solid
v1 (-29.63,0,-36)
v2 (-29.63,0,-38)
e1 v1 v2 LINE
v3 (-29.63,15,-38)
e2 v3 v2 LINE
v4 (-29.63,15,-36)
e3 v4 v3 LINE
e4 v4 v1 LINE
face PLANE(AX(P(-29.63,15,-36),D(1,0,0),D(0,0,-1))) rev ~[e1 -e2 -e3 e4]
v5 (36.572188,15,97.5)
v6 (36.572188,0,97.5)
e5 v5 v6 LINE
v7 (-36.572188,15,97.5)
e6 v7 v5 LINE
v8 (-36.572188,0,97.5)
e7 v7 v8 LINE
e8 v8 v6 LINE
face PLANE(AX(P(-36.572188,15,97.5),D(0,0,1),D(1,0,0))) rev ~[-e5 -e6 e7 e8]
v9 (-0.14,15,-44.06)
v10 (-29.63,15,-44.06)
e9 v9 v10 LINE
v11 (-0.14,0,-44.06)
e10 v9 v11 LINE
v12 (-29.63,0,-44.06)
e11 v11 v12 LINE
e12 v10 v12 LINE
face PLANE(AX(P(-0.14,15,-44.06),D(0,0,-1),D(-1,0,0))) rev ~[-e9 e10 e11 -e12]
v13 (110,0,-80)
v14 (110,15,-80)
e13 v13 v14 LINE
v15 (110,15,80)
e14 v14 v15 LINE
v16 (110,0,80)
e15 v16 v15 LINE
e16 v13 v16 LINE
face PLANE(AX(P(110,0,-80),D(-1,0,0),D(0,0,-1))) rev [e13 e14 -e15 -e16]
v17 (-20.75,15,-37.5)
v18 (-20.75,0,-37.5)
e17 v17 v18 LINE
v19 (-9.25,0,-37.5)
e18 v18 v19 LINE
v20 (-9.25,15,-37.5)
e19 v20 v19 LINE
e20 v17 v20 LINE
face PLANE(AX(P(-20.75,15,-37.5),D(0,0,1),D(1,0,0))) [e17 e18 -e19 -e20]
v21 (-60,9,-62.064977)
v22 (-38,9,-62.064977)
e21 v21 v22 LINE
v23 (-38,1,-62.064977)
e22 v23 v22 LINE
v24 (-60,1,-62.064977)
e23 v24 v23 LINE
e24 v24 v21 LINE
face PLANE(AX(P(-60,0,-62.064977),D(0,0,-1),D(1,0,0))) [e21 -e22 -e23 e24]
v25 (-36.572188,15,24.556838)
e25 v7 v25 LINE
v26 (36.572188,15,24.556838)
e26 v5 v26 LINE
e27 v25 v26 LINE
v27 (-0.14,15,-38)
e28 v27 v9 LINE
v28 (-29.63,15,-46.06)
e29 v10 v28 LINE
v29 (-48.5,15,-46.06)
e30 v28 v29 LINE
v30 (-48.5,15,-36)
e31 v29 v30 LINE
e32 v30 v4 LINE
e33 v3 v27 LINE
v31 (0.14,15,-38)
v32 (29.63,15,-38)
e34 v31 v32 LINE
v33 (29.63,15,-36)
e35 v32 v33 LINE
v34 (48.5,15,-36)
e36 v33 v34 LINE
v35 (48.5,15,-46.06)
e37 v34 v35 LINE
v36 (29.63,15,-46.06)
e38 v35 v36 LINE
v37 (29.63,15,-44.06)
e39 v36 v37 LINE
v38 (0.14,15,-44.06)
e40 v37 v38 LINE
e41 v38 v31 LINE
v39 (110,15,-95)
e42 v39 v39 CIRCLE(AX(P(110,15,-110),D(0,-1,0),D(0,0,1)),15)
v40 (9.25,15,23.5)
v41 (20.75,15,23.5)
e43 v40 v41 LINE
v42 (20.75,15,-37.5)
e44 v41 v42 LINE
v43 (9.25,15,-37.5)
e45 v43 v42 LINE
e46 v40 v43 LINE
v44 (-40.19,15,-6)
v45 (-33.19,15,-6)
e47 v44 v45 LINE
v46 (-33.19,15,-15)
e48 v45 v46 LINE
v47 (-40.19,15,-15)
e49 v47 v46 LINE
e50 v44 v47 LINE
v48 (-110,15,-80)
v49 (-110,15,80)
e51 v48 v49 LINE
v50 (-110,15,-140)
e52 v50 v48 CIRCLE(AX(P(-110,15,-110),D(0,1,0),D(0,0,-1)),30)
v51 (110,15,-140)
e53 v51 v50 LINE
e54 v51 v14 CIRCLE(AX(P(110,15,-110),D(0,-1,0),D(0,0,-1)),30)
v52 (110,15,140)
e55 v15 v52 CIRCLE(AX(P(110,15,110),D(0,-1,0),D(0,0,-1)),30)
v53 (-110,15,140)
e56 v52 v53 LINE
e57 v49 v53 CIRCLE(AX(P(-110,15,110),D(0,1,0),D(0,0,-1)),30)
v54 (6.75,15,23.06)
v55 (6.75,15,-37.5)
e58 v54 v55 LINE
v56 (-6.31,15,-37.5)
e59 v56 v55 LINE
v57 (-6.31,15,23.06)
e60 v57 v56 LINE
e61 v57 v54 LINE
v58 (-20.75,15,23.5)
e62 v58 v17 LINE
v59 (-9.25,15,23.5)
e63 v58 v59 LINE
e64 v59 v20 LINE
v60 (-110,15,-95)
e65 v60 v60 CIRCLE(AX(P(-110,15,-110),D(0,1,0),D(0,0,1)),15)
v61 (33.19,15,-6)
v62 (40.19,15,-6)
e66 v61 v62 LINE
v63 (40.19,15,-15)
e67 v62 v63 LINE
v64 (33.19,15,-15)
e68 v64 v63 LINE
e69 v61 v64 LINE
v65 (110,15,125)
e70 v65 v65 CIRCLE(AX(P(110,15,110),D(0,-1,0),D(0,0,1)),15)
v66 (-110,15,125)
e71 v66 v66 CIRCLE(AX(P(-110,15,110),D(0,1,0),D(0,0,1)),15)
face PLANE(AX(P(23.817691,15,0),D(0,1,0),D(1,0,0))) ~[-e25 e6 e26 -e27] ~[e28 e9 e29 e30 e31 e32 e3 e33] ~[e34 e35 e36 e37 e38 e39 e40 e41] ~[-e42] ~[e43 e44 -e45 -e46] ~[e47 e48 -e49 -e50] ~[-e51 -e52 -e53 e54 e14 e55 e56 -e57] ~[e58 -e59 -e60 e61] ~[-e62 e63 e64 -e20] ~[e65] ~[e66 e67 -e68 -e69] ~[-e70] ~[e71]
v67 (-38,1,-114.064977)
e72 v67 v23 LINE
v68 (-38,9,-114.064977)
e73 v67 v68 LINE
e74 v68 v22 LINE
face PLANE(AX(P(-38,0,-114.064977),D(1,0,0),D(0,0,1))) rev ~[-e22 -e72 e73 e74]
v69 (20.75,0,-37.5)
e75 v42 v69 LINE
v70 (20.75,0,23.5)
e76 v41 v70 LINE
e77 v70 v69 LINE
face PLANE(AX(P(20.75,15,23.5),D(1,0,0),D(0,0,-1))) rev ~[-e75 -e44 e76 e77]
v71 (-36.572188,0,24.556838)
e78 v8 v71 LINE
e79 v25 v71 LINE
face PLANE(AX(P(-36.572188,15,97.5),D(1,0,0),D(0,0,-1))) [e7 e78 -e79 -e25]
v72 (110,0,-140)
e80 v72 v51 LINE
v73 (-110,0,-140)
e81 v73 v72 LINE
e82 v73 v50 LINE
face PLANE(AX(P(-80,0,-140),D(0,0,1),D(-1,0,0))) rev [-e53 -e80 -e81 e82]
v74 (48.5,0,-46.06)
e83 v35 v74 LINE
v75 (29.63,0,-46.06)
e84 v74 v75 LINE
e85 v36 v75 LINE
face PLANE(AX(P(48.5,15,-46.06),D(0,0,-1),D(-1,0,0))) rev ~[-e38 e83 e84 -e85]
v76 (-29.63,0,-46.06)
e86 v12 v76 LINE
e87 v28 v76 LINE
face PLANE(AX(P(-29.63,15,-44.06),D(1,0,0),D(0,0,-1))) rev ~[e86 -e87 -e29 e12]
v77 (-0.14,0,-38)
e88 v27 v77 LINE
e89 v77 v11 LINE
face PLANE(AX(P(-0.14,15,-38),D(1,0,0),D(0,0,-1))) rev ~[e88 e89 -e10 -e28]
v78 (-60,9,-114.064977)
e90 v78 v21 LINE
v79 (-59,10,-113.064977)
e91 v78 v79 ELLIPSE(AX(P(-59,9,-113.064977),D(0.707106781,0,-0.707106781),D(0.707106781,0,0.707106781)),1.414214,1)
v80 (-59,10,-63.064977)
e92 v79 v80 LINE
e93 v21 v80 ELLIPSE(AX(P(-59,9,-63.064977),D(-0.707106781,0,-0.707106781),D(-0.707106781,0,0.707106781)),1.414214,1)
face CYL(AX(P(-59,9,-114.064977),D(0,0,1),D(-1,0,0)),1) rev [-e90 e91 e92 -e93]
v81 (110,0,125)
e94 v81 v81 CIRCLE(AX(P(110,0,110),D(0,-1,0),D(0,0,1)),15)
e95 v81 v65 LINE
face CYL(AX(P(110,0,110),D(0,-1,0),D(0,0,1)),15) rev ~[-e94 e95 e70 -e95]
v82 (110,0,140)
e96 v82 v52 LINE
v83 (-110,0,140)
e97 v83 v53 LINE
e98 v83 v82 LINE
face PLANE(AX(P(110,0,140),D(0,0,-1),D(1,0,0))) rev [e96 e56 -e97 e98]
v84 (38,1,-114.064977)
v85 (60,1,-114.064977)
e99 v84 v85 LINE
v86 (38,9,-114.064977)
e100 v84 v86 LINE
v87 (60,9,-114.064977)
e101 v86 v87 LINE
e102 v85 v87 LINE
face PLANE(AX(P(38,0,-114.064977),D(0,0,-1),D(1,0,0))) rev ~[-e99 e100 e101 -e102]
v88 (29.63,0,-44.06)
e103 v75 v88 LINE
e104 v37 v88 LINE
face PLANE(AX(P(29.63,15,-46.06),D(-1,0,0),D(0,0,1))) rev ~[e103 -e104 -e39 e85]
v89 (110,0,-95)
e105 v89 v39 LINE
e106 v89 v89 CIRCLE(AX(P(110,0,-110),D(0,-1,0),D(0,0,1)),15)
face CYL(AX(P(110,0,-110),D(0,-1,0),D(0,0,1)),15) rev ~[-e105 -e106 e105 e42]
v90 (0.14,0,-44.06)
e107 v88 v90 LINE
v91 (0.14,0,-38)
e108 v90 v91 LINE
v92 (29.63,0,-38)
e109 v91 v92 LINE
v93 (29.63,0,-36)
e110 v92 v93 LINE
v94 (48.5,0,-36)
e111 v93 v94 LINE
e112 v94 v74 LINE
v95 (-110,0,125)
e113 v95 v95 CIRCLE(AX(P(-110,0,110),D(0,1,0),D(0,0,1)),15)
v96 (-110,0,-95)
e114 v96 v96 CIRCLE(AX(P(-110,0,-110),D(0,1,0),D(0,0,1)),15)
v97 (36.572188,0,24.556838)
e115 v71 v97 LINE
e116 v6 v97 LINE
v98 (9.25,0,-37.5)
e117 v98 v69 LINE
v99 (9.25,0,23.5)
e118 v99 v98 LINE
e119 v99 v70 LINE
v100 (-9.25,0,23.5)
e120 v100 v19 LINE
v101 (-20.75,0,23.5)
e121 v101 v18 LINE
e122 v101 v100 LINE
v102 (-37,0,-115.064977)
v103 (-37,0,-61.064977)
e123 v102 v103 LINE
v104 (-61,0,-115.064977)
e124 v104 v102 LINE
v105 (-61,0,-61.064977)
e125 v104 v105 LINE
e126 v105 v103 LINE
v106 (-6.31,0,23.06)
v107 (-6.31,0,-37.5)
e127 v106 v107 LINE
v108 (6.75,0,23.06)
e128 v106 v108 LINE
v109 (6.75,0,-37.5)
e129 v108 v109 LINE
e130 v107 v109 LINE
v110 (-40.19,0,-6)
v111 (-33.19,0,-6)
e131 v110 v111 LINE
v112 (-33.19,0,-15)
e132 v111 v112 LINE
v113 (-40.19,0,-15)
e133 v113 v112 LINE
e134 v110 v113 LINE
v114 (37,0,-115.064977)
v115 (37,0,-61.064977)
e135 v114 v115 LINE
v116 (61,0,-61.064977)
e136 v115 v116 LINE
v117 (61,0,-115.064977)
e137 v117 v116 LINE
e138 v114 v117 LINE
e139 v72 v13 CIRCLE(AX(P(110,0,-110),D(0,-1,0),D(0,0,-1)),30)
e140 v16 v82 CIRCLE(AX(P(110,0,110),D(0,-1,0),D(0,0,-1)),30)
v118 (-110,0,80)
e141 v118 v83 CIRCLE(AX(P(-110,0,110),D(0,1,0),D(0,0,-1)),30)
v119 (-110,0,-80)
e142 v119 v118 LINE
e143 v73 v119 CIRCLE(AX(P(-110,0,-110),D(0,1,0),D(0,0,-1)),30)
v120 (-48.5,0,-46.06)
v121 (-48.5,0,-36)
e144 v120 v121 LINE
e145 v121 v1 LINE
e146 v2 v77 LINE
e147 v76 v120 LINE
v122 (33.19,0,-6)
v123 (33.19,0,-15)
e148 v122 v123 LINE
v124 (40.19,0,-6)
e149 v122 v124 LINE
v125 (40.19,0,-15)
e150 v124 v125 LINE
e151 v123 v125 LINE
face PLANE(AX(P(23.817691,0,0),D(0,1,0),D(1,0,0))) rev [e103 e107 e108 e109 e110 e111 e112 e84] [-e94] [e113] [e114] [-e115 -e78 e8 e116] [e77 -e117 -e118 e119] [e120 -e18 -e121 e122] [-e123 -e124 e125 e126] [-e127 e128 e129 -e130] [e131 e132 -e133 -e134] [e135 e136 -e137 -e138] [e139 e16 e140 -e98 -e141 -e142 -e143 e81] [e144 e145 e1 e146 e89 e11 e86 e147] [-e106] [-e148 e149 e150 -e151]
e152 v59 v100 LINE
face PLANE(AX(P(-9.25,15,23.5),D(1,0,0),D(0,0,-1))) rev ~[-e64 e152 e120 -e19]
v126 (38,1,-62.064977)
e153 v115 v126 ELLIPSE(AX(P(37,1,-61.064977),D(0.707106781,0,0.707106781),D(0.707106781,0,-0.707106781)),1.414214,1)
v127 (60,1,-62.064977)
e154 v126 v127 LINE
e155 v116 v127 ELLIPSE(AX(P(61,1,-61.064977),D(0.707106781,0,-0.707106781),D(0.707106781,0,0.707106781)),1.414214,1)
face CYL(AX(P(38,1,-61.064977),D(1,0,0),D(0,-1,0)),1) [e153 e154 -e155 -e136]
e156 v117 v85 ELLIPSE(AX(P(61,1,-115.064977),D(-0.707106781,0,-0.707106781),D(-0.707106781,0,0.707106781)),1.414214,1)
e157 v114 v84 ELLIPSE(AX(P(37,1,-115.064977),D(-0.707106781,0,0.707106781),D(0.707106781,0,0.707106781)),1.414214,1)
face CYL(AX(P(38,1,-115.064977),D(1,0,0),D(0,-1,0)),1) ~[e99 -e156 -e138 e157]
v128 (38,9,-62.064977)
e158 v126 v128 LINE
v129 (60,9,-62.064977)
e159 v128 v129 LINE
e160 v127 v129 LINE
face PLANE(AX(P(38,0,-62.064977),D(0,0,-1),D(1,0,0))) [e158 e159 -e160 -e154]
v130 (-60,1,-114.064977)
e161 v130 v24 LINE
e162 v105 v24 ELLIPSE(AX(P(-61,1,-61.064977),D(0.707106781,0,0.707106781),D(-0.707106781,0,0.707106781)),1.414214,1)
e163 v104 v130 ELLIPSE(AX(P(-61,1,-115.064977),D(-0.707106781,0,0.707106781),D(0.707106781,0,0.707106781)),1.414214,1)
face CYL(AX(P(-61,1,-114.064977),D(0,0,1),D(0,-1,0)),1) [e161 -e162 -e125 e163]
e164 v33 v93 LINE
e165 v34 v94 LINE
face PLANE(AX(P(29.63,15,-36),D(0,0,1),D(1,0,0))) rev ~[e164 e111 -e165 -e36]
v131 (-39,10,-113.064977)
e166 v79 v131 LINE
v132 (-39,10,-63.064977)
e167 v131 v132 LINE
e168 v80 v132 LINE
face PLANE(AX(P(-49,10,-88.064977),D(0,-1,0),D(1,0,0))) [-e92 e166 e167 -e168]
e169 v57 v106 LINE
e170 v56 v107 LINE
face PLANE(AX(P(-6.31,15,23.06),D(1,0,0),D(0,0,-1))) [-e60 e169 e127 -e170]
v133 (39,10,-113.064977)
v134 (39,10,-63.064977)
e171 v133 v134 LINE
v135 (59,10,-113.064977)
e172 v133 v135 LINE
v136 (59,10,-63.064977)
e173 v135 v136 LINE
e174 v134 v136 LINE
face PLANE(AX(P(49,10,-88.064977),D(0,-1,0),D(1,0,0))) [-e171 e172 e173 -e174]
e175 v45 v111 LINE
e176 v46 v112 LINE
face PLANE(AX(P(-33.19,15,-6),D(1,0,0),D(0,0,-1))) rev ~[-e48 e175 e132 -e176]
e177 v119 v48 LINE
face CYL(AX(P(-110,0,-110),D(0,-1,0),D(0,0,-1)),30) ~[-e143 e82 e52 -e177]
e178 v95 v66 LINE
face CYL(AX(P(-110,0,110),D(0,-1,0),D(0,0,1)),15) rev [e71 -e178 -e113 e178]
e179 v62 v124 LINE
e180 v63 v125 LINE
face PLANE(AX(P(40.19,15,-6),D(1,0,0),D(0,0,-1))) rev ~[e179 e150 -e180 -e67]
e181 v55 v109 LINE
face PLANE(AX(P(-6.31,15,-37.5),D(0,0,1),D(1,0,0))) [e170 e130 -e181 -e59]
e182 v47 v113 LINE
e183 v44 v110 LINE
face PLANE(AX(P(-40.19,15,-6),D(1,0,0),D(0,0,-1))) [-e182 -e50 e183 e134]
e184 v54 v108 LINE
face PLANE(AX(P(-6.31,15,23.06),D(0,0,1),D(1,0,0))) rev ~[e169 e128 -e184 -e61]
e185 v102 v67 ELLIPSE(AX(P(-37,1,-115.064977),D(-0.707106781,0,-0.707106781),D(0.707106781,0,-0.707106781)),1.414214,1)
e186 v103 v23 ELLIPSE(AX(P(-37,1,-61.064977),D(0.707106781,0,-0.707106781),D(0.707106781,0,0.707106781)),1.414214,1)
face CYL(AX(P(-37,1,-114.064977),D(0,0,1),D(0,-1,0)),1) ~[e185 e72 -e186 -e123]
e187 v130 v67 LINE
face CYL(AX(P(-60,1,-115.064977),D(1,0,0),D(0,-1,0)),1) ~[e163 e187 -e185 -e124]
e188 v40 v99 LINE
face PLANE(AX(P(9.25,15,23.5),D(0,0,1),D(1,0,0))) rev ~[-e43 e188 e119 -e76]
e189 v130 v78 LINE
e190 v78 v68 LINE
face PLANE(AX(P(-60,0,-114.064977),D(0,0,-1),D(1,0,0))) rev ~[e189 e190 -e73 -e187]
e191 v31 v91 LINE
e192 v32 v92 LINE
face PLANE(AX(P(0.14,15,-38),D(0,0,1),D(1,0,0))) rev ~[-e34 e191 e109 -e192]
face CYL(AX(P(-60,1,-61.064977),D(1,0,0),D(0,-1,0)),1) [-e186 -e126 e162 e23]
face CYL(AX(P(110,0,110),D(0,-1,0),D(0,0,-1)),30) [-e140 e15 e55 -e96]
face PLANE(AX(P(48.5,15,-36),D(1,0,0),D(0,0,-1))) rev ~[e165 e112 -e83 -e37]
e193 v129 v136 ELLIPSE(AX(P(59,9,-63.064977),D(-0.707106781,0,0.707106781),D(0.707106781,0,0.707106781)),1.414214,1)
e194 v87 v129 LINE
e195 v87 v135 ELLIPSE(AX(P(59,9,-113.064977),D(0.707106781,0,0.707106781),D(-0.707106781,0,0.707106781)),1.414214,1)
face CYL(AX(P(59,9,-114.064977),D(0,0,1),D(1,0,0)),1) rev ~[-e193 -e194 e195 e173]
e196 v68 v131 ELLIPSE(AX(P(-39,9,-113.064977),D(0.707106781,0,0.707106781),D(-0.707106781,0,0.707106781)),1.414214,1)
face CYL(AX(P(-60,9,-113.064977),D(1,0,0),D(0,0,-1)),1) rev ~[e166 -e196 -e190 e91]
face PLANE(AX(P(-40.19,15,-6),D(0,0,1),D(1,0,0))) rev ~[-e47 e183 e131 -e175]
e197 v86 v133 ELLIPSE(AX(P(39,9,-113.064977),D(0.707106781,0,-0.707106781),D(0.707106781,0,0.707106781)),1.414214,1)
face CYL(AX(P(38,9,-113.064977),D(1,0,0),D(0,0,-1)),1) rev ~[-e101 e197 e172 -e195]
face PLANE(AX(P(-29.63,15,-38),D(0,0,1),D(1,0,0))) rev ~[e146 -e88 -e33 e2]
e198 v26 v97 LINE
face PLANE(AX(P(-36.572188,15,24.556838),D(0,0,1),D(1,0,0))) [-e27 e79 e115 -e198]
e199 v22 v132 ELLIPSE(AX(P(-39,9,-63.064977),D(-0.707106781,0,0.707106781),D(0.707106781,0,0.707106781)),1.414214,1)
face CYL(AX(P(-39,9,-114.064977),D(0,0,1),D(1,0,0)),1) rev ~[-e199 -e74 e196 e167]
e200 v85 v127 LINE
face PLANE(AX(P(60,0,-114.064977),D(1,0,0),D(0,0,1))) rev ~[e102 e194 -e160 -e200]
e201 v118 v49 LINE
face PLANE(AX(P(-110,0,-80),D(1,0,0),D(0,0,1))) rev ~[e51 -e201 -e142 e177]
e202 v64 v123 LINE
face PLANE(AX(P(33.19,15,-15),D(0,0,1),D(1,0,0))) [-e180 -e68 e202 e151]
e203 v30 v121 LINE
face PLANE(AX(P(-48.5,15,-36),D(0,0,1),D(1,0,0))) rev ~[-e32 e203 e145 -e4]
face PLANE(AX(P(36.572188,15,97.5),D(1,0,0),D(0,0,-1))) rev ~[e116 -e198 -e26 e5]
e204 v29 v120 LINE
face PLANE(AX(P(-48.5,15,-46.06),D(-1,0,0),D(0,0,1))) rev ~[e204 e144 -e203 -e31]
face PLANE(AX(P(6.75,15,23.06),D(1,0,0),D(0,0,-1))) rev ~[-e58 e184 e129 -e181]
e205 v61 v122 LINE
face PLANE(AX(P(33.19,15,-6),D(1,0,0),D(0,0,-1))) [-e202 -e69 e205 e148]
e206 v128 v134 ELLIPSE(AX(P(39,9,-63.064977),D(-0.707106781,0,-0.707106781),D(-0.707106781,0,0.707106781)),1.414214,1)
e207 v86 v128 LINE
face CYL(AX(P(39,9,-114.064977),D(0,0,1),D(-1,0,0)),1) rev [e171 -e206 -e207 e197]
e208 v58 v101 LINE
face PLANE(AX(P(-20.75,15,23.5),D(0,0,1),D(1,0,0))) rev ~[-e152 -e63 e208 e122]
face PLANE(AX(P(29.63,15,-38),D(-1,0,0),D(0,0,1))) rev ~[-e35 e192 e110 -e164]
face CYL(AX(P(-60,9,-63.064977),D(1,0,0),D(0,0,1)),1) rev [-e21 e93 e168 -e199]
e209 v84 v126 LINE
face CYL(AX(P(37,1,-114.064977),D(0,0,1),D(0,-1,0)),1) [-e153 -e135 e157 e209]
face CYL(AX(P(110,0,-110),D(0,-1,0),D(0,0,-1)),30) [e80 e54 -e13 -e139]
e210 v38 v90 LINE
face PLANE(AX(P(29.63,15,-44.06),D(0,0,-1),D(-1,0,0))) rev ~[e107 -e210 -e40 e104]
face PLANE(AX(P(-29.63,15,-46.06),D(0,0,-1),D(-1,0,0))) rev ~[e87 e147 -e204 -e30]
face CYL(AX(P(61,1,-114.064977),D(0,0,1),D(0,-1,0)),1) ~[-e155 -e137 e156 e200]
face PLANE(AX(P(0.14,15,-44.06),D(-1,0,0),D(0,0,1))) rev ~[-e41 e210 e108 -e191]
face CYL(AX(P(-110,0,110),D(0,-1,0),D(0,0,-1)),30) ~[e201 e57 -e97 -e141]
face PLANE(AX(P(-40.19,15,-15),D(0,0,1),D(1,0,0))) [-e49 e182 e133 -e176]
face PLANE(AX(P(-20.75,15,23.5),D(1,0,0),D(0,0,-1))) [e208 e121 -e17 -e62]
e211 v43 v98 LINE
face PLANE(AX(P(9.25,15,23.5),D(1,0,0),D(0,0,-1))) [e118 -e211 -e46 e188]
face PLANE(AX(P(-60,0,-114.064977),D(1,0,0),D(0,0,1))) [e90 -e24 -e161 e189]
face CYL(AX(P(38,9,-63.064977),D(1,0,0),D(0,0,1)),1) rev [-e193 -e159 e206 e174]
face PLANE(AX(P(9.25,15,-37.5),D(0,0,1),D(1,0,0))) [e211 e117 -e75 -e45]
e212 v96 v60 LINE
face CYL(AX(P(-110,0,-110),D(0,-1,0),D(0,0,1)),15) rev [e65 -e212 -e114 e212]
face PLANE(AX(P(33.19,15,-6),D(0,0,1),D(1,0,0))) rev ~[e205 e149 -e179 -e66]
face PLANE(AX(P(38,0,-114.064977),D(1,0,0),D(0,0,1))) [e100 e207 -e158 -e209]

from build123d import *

# Parameters (mm, degrees)
SKETCH1_R           = 15
BOSS_EXTRUDE1_DEPTH = 15
CUT_EXTRUDE1_REACH  = 200.557
SKETCH6_W           = 73.144376366
SKETCH6_H           = 72.943161699
SKETCH6_W_2         = 11.5
SKETCH6_H_2         = 61
SKETCH6_W_3         = 13.06
SKETCH6_H_3         = 60.56
SKETCH6_W_4         = 7
SKETCH6_H_4         = 9
SKETCH7_W           = 22
SKETCH7_H           = 52
CUT_EXTRUDE2_DEPTH  = 10
FILLET1_R           = 1


with BuildPart() as part:
    # Sketch1 → Boss-Extrude1 (new body)
    with BuildSketch(Plane(origin=(0, 0, 0), x_dir=(1, 0, 0), z_dir=(0, 1, 0))):
        with BuildLine():
            Line((-110, -140), (80, -140))
            Line((80, -140), (80, 140))
            Line((80, 140), (-110, 140))
            ThreePointArc((-110, 140), (-140, 110), (-110, 80))
            Line((-110, 80), (-110, -80))
            ThreePointArc((-110, -80), (-140, -110), (-110, -140))
        make_face()
        with Locations(Location((-110, 110, 0), (0, 0, 270))):
            Circle(SKETCH1_R, mode=Mode.SUBTRACT)
        with Locations(Location((-110, -110, 0), (0, 0, 270))):
            Circle(SKETCH1_R, mode=Mode.SUBTRACT)
    boss_extrude1 = extrude(amount=BOSS_EXTRUDE1_DEPTH)

    # Mirror1: Boss-Extrude1 across plane
    add(boss_extrude1.mirror(Plane(origin=(0, 0, 0), x_dir=(0, 0, 1), z_dir=(1, 0, 0))))

    # Sketch6 → Cut-Extrude1 (cut, up to next)
    with BuildSketch(Plane(origin=(0, 15, 0), x_dir=(1, 0, 0), z_dir=(0, 1, 0)), mode=Mode.PRIVATE) as cut_extrude1_sk1:
        with Locations((0, -61.02841915)):
            Rectangle(SKETCH6_W, SKETCH6_H)
    cut_extrude1_tool1 = extrude(cut_extrude1_sk1.sketch, amount=-CUT_EXTRUDE1_REACH, mode=Mode.PRIVATE) & part.part
    # Sketch6 → Cut-Extrude1 (cut, up to next)
    with BuildSketch(Plane(origin=(0, 15, 0), x_dir=(1, 0, 0), z_dir=(0, 1, 0)), mode=Mode.PRIVATE) as cut_extrude1_sk2:
        with Locations((-15, 7)):
            Rectangle(SKETCH6_W_2, SKETCH6_H_2)
    cut_extrude1_tool2 = extrude(cut_extrude1_sk2.sketch, amount=-CUT_EXTRUDE1_REACH, mode=Mode.PRIVATE) & part.part
    # Sketch6 → Cut-Extrude1 (cut, up to next)
    with BuildSketch(Plane(origin=(0, 15, 0), x_dir=(1, 0, 0), z_dir=(0, 1, 0)), mode=Mode.PRIVATE) as cut_extrude1_sk3:
        Polygon((-0.14, 38), (-0.14, 44.06), (-29.63, 44.06), (-29.63, 46.06), (-48.5, 46.06), (-48.5, 36), (-29.63, 36), (-29.63, 38), align=None)
    cut_extrude1_tool3 = extrude(cut_extrude1_sk3.sketch, amount=-CUT_EXTRUDE1_REACH, mode=Mode.PRIVATE) & part.part
    # Sketch6 → Cut-Extrude1 (cut, up to next)
    with BuildSketch(Plane(origin=(0, 15, 0), x_dir=(1, 0, 0), z_dir=(0, 1, 0)), mode=Mode.PRIVATE) as cut_extrude1_sk4:
        Polygon((29.63, 36), (48.5, 36), (48.5, 46.06), (29.63, 46.06), (29.63, 44.06), (0.14, 44.06), (0.14, 38), (29.63, 38), align=None)
    cut_extrude1_tool4 = extrude(cut_extrude1_sk4.sketch, amount=-CUT_EXTRUDE1_REACH, mode=Mode.PRIVATE) & part.part
    # Sketch6 → Cut-Extrude1 (cut, up to next)
    with BuildSketch(Plane(origin=(0, 15, 0), x_dir=(1, 0, 0), z_dir=(0, 1, 0)), mode=Mode.PRIVATE) as cut_extrude1_sk5:
        with Locations((0.22, 7.22)):
            Rectangle(SKETCH6_W_3, SKETCH6_H_3)
    cut_extrude1_tool5 = extrude(cut_extrude1_sk5.sketch, amount=-CUT_EXTRUDE1_REACH, mode=Mode.PRIVATE) & part.part
    # Sketch6 → Cut-Extrude1 (cut, up to next)
    with BuildSketch(Plane(origin=(0, 15, 0), x_dir=(1, 0, 0), z_dir=(0, 1, 0)), mode=Mode.PRIVATE) as cut_extrude1_sk6:
        with Locations((15, 7)):
            Rectangle(SKETCH6_W_2, SKETCH6_H_2)
    cut_extrude1_tool6 = extrude(cut_extrude1_sk6.sketch, amount=-CUT_EXTRUDE1_REACH, mode=Mode.PRIVATE) & part.part
    # Sketch6 → Cut-Extrude1 (cut, up to next)
    with BuildSketch(Plane(origin=(0, 15, 0), x_dir=(1, 0, 0), z_dir=(0, 1, 0)), mode=Mode.PRIVATE) as cut_extrude1_sk7:
        with Locations((-36.69, 10.5)):
            Rectangle(SKETCH6_W_4, SKETCH6_H_4)
    cut_extrude1_tool7 = extrude(cut_extrude1_sk7.sketch, amount=-CUT_EXTRUDE1_REACH, mode=Mode.PRIVATE) & part.part
    # Sketch6 → Cut-Extrude1 (cut, up to next)
    with BuildSketch(Plane(origin=(0, 15, 0), x_dir=(1, 0, 0), z_dir=(0, 1, 0)), mode=Mode.PRIVATE) as cut_extrude1_sk8:
        with Locations((36.69, 10.5)):
            Rectangle(SKETCH6_W_4, SKETCH6_H_4)
    cut_extrude1_tool8 = extrude(cut_extrude1_sk8.sketch, amount=-CUT_EXTRUDE1_REACH, mode=Mode.PRIVATE) & part.part
    add(cut_extrude1_tool1.solids().sort_by_distance((0, 15, 61.028419))[0], mode=Mode.SUBTRACT)
    add(cut_extrude1_tool2.solids().sort_by_distance((-15, 15, -7))[0], mode=Mode.SUBTRACT)
    add(cut_extrude1_tool3.solids().sort_by_distance((-27.339883, 15, -41.03))[0], mode=Mode.SUBTRACT)
    add(cut_extrude1_tool4.solids().sort_by_distance((27.339883, 15, -41.03))[0], mode=Mode.SUBTRACT)
    add(cut_extrude1_tool5.solids().sort_by_distance((0.22, 15, -7.22))[0], mode=Mode.SUBTRACT)
    add(cut_extrude1_tool6.solids().sort_by_distance((15, 15, -7))[0], mode=Mode.SUBTRACT)
    add(cut_extrude1_tool7.solids().sort_by_distance((-36.69, 15, -10.5))[0], mode=Mode.SUBTRACT)
    add(cut_extrude1_tool8.solids().sort_by_distance((36.69, 15, -10.5))[0], mode=Mode.SUBTRACT)

    # Sketch7 → Cut-Extrude2 (cut)
    with BuildSketch(Plane.XZ):
        with Locations((49, -88.06497659)):
            Rectangle(SKETCH7_W, SKETCH7_H)
        with Locations((-49, -88.06497659)):
            Rectangle(SKETCH7_W, SKETCH7_H)
    extrude(amount=-CUT_EXTRUDE2_DEPTH, mode=Mode.SUBTRACT)

    # Fillet1
    fillet1_edges = [part.edges().sort_by_distance(p)[0] for p in [
        (60, 10, -88.06497659),
        (49, 10, -114.06497659),
        (38, 10, -88.06497659),
        (49, 10, -62.06497659),
        (60, 0, -88.06497659),
        (49, 0, -62.06497659),
        (38, 0, -88.06497659),
        (49, 0, -114.06497659),
        (-60, 10, -88.06497659),
        (-49, 10, -62.06497659),
        (-38, 10, -88.06497659),
        (-49, 10, -114.06497659),
        (-60, 0, -88.06497659),
        (-49, 0, -114.06497659),
        (-38, 0, -88.06497659),
        (-49, 0, -62.06497659),
    ]]
    fillet(fillet1_edges, radius=FILLET1_R)


solid = part.part
